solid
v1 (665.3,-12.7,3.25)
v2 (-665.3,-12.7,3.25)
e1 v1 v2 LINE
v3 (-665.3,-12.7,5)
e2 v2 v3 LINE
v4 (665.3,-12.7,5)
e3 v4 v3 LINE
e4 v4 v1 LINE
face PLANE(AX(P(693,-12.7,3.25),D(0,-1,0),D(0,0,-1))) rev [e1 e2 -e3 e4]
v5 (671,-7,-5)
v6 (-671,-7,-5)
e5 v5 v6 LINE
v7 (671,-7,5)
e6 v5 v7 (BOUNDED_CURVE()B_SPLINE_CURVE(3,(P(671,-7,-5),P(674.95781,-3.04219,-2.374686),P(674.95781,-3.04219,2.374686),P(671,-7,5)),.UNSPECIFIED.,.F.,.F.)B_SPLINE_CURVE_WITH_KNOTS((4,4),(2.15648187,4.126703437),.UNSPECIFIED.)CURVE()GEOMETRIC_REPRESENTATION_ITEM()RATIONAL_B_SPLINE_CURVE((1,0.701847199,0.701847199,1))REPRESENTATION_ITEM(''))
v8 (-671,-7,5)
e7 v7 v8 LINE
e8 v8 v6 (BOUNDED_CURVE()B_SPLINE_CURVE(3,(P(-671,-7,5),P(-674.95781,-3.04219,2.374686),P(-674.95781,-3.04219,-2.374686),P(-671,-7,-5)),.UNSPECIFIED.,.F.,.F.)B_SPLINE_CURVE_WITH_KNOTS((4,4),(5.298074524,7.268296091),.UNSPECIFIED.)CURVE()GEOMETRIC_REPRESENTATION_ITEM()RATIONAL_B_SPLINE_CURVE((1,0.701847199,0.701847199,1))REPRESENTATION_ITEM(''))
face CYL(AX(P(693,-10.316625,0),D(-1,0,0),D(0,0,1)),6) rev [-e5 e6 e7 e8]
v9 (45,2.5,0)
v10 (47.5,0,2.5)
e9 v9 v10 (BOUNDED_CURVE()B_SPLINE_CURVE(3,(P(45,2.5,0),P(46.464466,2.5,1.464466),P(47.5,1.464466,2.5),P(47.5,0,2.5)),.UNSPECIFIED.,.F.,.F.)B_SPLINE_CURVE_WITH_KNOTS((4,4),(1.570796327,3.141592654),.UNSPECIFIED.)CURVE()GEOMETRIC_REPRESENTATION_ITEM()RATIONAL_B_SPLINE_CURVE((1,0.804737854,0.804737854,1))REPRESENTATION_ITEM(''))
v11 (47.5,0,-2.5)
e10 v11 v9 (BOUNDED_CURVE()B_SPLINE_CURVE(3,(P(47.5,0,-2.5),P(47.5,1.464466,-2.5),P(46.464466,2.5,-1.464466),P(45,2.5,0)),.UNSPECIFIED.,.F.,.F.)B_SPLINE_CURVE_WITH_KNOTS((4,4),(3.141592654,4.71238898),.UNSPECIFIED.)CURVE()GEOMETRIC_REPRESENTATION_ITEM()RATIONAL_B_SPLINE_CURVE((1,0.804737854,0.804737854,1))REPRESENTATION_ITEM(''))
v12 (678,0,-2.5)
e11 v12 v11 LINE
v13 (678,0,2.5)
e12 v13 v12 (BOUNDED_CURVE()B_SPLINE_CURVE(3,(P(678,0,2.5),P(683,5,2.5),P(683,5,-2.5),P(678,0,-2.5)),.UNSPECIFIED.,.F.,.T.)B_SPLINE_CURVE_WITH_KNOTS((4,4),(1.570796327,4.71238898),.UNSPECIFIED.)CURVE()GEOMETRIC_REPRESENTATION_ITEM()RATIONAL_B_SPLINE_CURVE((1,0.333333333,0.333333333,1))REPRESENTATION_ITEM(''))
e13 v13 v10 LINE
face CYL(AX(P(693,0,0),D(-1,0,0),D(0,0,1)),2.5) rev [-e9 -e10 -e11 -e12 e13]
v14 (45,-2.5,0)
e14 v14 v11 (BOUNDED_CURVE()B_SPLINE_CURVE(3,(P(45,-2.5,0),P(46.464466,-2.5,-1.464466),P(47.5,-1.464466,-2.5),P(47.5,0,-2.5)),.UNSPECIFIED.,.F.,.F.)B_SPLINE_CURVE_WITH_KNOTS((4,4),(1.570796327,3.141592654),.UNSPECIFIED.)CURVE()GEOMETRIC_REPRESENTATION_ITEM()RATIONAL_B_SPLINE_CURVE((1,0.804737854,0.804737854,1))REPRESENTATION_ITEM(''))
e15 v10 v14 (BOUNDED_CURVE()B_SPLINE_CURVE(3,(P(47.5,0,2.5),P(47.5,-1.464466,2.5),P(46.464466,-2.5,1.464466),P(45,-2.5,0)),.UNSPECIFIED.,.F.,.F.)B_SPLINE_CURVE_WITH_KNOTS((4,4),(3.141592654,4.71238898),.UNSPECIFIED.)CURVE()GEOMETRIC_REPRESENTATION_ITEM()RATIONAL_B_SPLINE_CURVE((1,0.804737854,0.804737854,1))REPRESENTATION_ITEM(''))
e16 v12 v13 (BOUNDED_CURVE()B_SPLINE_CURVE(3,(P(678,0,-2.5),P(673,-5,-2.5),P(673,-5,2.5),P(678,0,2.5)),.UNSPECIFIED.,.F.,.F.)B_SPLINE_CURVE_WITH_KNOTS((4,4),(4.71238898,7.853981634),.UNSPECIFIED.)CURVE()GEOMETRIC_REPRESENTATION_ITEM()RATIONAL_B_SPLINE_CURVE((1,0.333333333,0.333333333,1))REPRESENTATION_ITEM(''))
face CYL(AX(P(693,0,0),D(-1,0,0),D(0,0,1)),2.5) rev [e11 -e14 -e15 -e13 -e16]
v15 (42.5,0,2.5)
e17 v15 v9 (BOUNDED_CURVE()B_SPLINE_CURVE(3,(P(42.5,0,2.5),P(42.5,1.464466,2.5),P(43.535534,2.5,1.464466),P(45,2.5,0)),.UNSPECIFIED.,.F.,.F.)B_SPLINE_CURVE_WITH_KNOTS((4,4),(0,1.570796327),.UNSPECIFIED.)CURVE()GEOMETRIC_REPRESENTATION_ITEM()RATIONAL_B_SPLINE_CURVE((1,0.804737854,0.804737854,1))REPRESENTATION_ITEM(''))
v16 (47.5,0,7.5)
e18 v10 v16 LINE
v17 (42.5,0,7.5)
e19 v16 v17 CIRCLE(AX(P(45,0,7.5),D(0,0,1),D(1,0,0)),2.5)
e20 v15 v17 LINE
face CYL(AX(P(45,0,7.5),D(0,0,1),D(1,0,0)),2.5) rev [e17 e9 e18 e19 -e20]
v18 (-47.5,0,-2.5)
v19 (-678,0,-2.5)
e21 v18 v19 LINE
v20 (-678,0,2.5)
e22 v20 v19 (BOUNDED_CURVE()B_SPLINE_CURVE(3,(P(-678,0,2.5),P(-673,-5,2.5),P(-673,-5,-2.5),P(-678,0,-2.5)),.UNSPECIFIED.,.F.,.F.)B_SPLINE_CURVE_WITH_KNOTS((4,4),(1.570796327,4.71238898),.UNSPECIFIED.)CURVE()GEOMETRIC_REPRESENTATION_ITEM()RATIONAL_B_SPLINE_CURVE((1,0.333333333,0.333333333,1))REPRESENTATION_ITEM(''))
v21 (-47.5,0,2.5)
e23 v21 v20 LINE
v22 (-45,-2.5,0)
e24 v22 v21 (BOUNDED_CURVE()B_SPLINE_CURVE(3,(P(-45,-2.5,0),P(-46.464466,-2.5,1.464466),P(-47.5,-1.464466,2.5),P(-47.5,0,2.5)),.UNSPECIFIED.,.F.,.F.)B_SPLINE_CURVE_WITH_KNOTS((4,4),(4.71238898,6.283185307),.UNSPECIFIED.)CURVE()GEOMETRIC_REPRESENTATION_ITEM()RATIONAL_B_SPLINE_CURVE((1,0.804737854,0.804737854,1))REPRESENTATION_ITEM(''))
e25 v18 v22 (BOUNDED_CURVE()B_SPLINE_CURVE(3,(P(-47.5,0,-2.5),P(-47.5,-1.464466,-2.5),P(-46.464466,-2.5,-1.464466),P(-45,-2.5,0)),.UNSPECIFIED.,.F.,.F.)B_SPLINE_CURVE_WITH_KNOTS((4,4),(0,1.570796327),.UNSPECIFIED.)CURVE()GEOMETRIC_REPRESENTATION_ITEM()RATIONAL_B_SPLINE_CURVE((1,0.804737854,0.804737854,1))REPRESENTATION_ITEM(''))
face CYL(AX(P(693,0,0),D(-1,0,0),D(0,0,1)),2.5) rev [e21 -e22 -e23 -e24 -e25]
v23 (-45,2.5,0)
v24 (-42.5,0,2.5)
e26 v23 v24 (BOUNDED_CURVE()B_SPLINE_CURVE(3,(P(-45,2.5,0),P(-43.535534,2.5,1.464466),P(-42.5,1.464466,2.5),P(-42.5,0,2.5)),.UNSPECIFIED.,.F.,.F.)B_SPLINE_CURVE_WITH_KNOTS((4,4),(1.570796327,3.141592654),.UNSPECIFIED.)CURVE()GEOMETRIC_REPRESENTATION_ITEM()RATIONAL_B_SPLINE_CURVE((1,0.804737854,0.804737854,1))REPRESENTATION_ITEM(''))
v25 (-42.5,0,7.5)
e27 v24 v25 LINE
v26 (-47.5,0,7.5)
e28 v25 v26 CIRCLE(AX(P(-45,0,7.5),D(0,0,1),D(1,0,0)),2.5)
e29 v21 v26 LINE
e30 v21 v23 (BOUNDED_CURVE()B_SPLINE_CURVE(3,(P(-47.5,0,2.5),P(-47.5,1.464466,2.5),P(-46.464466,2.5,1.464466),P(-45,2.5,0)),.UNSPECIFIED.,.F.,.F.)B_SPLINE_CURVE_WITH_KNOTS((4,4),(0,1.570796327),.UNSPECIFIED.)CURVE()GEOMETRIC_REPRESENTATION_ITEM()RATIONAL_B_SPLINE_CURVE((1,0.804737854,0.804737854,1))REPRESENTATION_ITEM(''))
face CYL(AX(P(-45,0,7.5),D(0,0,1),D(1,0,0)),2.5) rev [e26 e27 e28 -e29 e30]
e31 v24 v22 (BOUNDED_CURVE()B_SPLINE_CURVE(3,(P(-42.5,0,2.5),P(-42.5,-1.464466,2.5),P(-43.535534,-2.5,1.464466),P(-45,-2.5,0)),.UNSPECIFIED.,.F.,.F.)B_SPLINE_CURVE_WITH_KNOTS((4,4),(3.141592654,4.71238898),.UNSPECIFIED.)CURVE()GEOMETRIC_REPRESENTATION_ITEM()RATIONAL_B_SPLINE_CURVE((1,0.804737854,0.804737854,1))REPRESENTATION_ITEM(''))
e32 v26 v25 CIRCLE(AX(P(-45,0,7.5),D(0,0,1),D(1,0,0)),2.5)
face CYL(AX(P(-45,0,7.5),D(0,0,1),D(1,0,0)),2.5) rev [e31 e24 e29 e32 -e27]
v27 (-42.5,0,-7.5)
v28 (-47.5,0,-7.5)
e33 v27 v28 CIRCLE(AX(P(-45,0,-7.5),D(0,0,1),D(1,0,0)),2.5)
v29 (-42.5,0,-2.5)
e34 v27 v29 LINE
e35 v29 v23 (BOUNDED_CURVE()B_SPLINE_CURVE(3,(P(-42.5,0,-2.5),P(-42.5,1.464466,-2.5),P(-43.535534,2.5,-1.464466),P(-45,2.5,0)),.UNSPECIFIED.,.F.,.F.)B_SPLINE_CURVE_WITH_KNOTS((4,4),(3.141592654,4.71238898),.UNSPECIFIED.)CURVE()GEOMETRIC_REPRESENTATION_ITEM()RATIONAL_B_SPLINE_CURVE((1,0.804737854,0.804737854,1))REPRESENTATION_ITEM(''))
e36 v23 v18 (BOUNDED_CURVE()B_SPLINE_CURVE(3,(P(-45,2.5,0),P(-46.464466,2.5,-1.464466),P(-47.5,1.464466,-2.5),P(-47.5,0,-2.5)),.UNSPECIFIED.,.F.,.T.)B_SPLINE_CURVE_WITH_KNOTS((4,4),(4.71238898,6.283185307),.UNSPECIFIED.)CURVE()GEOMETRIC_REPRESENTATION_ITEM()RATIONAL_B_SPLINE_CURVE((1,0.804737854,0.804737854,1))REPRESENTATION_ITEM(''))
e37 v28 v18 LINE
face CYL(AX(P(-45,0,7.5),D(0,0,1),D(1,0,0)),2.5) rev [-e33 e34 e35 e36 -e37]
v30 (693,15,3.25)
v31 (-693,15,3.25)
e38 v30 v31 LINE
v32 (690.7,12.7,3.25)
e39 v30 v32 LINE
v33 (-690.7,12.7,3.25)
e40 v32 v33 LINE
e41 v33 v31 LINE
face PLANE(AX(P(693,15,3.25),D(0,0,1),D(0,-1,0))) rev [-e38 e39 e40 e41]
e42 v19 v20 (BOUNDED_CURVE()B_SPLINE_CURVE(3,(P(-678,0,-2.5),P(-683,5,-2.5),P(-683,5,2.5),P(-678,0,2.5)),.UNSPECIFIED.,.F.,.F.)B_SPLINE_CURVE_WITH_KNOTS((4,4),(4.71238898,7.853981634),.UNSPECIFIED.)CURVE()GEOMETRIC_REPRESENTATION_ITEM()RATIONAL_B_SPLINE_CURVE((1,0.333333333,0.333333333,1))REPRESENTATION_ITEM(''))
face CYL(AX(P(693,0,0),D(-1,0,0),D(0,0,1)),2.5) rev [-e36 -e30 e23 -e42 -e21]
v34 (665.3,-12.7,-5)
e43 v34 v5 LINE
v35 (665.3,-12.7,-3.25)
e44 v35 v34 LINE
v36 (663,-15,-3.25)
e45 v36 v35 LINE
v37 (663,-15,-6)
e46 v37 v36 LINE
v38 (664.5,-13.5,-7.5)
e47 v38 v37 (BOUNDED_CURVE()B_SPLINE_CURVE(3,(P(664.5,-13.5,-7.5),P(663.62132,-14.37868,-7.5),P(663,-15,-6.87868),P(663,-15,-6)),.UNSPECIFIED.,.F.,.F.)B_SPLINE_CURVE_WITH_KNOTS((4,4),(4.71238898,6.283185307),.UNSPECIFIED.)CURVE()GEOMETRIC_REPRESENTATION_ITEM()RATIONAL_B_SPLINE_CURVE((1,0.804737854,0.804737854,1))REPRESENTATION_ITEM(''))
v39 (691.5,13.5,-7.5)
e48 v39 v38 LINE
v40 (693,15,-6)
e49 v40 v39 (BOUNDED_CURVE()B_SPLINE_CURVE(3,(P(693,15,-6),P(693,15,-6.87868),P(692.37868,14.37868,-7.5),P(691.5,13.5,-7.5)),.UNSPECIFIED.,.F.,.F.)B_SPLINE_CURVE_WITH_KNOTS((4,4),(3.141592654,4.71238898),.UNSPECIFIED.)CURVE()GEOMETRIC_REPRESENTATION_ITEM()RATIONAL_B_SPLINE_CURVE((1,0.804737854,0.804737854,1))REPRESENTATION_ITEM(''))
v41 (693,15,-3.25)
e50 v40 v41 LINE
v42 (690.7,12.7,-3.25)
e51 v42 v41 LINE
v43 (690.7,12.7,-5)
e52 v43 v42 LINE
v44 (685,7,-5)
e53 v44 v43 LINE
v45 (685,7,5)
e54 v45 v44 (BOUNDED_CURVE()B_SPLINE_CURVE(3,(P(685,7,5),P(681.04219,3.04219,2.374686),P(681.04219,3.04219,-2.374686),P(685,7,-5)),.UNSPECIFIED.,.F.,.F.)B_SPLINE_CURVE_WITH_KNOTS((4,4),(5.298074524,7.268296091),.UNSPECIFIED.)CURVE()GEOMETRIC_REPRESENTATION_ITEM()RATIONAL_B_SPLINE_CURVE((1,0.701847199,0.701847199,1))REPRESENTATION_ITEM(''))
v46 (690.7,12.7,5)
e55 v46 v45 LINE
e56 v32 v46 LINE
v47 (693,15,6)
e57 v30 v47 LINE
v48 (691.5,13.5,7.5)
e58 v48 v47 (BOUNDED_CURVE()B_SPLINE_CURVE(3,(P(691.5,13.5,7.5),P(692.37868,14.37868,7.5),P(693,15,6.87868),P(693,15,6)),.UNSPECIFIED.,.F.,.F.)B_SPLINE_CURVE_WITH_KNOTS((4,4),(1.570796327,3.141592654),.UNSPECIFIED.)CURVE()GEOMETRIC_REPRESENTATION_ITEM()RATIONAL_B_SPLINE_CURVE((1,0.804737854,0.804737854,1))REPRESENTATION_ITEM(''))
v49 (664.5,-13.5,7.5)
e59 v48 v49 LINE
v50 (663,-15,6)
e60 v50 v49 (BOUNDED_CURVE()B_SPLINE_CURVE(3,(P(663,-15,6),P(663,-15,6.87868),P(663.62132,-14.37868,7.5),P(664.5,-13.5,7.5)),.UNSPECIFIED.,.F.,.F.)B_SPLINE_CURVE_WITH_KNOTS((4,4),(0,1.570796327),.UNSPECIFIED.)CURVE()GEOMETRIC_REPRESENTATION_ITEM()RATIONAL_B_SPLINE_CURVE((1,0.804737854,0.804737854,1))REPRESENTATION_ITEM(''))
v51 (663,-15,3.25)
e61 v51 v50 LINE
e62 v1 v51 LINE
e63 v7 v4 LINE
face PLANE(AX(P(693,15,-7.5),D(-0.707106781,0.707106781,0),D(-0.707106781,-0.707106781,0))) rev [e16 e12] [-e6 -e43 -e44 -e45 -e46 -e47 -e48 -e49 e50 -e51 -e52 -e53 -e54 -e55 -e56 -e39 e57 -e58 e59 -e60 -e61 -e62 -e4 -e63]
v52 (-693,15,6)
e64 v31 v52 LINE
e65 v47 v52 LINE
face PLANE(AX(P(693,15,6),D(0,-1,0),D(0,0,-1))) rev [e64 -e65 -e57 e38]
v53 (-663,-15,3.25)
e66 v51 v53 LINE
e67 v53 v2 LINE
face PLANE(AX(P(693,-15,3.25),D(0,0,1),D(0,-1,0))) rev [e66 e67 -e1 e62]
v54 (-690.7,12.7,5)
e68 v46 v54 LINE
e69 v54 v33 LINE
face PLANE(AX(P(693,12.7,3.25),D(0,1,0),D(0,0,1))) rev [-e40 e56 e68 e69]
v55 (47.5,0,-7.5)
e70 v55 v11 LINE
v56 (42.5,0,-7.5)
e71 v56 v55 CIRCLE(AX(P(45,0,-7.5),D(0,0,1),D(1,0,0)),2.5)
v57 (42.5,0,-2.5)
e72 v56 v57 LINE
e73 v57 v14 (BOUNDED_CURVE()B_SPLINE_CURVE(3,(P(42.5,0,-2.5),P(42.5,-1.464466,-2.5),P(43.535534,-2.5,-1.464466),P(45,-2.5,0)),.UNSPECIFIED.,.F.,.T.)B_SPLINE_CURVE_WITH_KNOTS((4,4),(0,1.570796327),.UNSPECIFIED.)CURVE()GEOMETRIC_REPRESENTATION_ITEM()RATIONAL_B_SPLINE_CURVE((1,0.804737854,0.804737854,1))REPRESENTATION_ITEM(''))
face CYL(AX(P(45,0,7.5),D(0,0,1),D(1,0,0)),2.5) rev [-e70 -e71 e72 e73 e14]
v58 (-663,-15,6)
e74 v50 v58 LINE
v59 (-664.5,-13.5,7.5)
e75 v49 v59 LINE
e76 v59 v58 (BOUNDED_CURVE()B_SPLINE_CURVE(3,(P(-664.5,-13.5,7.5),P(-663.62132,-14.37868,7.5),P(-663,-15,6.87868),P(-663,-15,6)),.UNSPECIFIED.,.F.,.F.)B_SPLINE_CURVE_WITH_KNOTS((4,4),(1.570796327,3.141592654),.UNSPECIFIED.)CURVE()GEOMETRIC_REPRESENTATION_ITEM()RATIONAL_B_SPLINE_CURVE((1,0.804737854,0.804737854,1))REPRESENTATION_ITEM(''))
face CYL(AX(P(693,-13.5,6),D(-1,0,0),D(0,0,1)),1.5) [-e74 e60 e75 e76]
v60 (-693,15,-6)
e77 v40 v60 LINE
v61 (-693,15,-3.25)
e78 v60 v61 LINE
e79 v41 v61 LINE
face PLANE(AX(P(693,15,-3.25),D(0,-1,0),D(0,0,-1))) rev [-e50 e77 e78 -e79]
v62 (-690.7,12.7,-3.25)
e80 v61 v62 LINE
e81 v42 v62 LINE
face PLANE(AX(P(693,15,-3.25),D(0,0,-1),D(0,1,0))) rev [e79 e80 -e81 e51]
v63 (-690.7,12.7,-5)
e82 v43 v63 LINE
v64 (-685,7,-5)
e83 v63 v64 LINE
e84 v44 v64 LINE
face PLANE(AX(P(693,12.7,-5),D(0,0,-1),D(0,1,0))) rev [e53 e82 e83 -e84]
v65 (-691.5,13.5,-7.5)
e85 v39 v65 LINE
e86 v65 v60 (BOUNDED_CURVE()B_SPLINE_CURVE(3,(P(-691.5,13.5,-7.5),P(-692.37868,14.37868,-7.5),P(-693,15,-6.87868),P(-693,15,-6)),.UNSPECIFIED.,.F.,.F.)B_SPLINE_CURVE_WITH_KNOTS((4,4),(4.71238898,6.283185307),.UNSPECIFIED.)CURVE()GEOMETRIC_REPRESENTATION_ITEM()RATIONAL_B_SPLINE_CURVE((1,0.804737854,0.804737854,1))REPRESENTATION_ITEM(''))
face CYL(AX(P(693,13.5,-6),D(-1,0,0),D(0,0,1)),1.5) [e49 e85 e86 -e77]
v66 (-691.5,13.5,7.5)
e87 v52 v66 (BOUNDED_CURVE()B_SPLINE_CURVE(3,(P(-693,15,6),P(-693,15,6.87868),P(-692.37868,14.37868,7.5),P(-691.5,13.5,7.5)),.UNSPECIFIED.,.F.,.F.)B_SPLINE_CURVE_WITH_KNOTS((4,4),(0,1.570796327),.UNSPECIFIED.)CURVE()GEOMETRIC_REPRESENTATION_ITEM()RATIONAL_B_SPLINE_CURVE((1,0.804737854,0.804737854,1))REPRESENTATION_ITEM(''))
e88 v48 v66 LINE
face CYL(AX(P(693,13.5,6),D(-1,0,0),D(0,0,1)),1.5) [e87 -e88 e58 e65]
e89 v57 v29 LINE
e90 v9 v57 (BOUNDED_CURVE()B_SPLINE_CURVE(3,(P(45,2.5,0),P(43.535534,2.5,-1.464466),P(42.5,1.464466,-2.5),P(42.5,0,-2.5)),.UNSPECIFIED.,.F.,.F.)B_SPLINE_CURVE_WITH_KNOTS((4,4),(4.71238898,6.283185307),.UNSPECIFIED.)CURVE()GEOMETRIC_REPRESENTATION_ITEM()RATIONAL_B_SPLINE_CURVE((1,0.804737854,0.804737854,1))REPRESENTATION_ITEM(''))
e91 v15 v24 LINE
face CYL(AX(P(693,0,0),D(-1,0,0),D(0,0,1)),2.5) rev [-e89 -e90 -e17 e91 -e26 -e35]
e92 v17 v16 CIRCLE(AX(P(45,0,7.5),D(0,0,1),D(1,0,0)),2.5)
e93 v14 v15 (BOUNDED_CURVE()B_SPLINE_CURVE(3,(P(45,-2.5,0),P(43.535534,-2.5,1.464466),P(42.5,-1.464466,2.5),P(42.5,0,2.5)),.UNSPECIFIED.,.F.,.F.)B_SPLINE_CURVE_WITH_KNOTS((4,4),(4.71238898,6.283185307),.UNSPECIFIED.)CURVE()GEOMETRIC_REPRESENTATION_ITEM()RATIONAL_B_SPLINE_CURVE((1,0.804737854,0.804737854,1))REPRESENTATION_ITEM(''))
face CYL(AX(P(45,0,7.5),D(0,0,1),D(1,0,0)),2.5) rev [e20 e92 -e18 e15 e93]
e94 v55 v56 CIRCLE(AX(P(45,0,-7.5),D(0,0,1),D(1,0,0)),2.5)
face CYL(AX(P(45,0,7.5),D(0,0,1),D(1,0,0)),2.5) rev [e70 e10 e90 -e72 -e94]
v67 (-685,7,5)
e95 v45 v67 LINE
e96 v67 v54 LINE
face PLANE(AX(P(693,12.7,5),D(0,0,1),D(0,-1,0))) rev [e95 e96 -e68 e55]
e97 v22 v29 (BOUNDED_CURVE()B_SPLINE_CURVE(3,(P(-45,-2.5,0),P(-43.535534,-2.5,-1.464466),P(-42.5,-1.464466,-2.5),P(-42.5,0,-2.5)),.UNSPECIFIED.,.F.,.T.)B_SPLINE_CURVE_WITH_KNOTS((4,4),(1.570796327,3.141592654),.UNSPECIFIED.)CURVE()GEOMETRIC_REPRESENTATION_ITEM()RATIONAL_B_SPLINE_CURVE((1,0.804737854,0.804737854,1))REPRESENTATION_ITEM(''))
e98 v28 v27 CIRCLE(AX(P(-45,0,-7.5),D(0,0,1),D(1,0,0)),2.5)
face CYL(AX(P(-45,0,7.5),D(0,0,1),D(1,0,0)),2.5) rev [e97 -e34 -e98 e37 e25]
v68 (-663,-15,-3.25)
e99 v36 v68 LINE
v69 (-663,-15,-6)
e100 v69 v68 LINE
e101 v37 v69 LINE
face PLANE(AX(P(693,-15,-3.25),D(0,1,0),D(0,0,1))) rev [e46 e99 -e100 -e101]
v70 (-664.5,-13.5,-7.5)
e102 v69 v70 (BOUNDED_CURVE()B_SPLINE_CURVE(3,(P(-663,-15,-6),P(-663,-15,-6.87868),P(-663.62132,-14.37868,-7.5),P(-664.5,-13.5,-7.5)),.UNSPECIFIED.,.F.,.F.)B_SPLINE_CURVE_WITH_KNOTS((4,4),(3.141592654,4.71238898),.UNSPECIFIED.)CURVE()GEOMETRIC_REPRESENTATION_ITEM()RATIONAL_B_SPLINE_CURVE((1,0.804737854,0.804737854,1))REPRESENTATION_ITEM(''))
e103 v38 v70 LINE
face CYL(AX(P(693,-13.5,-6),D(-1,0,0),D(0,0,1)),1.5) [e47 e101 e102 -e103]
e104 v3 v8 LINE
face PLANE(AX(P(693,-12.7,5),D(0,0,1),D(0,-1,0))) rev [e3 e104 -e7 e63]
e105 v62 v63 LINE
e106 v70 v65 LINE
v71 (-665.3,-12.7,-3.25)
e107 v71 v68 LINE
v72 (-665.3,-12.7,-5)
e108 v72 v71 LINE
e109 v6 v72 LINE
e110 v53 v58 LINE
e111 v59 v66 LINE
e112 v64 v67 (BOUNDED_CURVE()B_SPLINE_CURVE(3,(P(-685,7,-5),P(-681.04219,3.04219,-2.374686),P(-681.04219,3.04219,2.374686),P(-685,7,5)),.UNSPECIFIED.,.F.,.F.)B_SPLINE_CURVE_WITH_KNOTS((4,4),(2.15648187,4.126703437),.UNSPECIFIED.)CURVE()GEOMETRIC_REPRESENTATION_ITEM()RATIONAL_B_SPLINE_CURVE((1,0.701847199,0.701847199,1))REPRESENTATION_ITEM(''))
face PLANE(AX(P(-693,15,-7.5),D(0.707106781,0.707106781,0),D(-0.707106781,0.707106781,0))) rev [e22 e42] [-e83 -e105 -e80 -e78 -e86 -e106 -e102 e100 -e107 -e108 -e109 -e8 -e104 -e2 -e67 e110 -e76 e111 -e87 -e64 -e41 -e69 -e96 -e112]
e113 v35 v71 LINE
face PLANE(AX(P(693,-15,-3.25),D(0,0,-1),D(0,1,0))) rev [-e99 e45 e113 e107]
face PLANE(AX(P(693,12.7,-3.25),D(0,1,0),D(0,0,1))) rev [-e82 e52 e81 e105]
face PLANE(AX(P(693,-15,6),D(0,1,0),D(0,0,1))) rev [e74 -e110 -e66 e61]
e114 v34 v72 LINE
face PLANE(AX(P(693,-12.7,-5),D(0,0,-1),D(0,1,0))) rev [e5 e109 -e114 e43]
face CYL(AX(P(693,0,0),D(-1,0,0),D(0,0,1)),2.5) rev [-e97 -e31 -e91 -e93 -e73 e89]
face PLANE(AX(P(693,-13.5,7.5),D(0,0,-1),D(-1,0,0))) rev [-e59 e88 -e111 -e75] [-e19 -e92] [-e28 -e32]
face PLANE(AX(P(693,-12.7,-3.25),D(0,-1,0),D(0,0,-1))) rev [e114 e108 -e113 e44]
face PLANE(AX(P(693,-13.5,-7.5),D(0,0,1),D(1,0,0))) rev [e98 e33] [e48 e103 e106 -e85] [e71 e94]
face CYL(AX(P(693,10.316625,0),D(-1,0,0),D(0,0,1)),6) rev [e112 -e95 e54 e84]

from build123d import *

# Parameters (mm, degrees)
SKETCH11_R          = 2.5
MEMBER_1_DEPTH      = 1386
CUT_EXTRUDE_1_DEPTH = 694.324599304
HOLE_WIZARD_M6_1_D  = 5


with BuildPart() as part:
    # Sketch11 → Member 1 (new body)
    with BuildSketch(Plane(origin=(-693, 0, 0), x_dir=(0, 0, -1), z_dir=(1, 0, 0))):
        with BuildLine():
            Line((-6, -15), (-3.25, -15))
            Line((-3.25, -15), (-3.25, -12.7))
            Line((-3.25, -12.7), (-5, -12.7))
            Line((-5, -12.7), (-5, -7))
            ThreePointArc((-5, -7), (0, -4.31662479), (5, -7))
            Line((5, -7), (5, -12.7))
            Line((5, -12.7), (3.25, -12.7))
            Line((3.25, -12.7), (3.25, -15))
            Line((3.25, -15), (6, -15))
            ThreePointArc((6, -15), (7.060660172, -14.560660172), (7.5, -13.5))
            Line((7.5, -13.5), (7.5, 13.5))
            ThreePointArc((7.5, 13.5), (7.060660172, 14.560660172), (6, 15))
            Line((6, 15), (3.25, 15))
            Line((3.25, 15), (3.25, 12.7))
            Line((3.25, 12.7), (5, 12.7))
            Line((5, 12.7), (5, 7))
            ThreePointArc((5, 7), (0, 4.31662479), (-5, 7))
            Line((-5, 7), (-5, 12.7))
            Line((-5, 12.7), (-3.25, 12.7))
            Line((-3.25, 12.7), (-3.25, 15))
            Line((-3.25, 15), (-6, 15))
            ThreePointArc((-6, 15), (-7.060660172, 14.560660172), (-7.5, 13.5))
            Line((-7.5, 13.5), (-7.5, -13.5))
            ThreePointArc((-7.5, -13.5), (-7.060660172, -14.560660172), (-6, -15))
        make_face()
        Circle(SKETCH11_R, mode=Mode.SUBTRACT)
    extrude(amount=MEMBER_1_DEPTH)

    # 草图4 → 切除-拉伸1 (cut, through all)
    with BuildSketch(Plane.XY.offset(7.5)):
        Polygon((-693, 15), (-663, -15), (-693, -15), align=None)
        Polygon((693, -15), (693, 15), (663, -15), align=None)
    extrude(amount=-CUT_EXTRUDE_1_DEPTH, mode=Mode.SUBTRACT)

    # M6 螺纹孔1 (through all)
    with Locations(Plane.XY.offset(7.5)):
        with Locations((-45, 0), (45, 0)):
            Hole(HOLE_WIZARD_M6_1_D / 2)


solid = part.part
